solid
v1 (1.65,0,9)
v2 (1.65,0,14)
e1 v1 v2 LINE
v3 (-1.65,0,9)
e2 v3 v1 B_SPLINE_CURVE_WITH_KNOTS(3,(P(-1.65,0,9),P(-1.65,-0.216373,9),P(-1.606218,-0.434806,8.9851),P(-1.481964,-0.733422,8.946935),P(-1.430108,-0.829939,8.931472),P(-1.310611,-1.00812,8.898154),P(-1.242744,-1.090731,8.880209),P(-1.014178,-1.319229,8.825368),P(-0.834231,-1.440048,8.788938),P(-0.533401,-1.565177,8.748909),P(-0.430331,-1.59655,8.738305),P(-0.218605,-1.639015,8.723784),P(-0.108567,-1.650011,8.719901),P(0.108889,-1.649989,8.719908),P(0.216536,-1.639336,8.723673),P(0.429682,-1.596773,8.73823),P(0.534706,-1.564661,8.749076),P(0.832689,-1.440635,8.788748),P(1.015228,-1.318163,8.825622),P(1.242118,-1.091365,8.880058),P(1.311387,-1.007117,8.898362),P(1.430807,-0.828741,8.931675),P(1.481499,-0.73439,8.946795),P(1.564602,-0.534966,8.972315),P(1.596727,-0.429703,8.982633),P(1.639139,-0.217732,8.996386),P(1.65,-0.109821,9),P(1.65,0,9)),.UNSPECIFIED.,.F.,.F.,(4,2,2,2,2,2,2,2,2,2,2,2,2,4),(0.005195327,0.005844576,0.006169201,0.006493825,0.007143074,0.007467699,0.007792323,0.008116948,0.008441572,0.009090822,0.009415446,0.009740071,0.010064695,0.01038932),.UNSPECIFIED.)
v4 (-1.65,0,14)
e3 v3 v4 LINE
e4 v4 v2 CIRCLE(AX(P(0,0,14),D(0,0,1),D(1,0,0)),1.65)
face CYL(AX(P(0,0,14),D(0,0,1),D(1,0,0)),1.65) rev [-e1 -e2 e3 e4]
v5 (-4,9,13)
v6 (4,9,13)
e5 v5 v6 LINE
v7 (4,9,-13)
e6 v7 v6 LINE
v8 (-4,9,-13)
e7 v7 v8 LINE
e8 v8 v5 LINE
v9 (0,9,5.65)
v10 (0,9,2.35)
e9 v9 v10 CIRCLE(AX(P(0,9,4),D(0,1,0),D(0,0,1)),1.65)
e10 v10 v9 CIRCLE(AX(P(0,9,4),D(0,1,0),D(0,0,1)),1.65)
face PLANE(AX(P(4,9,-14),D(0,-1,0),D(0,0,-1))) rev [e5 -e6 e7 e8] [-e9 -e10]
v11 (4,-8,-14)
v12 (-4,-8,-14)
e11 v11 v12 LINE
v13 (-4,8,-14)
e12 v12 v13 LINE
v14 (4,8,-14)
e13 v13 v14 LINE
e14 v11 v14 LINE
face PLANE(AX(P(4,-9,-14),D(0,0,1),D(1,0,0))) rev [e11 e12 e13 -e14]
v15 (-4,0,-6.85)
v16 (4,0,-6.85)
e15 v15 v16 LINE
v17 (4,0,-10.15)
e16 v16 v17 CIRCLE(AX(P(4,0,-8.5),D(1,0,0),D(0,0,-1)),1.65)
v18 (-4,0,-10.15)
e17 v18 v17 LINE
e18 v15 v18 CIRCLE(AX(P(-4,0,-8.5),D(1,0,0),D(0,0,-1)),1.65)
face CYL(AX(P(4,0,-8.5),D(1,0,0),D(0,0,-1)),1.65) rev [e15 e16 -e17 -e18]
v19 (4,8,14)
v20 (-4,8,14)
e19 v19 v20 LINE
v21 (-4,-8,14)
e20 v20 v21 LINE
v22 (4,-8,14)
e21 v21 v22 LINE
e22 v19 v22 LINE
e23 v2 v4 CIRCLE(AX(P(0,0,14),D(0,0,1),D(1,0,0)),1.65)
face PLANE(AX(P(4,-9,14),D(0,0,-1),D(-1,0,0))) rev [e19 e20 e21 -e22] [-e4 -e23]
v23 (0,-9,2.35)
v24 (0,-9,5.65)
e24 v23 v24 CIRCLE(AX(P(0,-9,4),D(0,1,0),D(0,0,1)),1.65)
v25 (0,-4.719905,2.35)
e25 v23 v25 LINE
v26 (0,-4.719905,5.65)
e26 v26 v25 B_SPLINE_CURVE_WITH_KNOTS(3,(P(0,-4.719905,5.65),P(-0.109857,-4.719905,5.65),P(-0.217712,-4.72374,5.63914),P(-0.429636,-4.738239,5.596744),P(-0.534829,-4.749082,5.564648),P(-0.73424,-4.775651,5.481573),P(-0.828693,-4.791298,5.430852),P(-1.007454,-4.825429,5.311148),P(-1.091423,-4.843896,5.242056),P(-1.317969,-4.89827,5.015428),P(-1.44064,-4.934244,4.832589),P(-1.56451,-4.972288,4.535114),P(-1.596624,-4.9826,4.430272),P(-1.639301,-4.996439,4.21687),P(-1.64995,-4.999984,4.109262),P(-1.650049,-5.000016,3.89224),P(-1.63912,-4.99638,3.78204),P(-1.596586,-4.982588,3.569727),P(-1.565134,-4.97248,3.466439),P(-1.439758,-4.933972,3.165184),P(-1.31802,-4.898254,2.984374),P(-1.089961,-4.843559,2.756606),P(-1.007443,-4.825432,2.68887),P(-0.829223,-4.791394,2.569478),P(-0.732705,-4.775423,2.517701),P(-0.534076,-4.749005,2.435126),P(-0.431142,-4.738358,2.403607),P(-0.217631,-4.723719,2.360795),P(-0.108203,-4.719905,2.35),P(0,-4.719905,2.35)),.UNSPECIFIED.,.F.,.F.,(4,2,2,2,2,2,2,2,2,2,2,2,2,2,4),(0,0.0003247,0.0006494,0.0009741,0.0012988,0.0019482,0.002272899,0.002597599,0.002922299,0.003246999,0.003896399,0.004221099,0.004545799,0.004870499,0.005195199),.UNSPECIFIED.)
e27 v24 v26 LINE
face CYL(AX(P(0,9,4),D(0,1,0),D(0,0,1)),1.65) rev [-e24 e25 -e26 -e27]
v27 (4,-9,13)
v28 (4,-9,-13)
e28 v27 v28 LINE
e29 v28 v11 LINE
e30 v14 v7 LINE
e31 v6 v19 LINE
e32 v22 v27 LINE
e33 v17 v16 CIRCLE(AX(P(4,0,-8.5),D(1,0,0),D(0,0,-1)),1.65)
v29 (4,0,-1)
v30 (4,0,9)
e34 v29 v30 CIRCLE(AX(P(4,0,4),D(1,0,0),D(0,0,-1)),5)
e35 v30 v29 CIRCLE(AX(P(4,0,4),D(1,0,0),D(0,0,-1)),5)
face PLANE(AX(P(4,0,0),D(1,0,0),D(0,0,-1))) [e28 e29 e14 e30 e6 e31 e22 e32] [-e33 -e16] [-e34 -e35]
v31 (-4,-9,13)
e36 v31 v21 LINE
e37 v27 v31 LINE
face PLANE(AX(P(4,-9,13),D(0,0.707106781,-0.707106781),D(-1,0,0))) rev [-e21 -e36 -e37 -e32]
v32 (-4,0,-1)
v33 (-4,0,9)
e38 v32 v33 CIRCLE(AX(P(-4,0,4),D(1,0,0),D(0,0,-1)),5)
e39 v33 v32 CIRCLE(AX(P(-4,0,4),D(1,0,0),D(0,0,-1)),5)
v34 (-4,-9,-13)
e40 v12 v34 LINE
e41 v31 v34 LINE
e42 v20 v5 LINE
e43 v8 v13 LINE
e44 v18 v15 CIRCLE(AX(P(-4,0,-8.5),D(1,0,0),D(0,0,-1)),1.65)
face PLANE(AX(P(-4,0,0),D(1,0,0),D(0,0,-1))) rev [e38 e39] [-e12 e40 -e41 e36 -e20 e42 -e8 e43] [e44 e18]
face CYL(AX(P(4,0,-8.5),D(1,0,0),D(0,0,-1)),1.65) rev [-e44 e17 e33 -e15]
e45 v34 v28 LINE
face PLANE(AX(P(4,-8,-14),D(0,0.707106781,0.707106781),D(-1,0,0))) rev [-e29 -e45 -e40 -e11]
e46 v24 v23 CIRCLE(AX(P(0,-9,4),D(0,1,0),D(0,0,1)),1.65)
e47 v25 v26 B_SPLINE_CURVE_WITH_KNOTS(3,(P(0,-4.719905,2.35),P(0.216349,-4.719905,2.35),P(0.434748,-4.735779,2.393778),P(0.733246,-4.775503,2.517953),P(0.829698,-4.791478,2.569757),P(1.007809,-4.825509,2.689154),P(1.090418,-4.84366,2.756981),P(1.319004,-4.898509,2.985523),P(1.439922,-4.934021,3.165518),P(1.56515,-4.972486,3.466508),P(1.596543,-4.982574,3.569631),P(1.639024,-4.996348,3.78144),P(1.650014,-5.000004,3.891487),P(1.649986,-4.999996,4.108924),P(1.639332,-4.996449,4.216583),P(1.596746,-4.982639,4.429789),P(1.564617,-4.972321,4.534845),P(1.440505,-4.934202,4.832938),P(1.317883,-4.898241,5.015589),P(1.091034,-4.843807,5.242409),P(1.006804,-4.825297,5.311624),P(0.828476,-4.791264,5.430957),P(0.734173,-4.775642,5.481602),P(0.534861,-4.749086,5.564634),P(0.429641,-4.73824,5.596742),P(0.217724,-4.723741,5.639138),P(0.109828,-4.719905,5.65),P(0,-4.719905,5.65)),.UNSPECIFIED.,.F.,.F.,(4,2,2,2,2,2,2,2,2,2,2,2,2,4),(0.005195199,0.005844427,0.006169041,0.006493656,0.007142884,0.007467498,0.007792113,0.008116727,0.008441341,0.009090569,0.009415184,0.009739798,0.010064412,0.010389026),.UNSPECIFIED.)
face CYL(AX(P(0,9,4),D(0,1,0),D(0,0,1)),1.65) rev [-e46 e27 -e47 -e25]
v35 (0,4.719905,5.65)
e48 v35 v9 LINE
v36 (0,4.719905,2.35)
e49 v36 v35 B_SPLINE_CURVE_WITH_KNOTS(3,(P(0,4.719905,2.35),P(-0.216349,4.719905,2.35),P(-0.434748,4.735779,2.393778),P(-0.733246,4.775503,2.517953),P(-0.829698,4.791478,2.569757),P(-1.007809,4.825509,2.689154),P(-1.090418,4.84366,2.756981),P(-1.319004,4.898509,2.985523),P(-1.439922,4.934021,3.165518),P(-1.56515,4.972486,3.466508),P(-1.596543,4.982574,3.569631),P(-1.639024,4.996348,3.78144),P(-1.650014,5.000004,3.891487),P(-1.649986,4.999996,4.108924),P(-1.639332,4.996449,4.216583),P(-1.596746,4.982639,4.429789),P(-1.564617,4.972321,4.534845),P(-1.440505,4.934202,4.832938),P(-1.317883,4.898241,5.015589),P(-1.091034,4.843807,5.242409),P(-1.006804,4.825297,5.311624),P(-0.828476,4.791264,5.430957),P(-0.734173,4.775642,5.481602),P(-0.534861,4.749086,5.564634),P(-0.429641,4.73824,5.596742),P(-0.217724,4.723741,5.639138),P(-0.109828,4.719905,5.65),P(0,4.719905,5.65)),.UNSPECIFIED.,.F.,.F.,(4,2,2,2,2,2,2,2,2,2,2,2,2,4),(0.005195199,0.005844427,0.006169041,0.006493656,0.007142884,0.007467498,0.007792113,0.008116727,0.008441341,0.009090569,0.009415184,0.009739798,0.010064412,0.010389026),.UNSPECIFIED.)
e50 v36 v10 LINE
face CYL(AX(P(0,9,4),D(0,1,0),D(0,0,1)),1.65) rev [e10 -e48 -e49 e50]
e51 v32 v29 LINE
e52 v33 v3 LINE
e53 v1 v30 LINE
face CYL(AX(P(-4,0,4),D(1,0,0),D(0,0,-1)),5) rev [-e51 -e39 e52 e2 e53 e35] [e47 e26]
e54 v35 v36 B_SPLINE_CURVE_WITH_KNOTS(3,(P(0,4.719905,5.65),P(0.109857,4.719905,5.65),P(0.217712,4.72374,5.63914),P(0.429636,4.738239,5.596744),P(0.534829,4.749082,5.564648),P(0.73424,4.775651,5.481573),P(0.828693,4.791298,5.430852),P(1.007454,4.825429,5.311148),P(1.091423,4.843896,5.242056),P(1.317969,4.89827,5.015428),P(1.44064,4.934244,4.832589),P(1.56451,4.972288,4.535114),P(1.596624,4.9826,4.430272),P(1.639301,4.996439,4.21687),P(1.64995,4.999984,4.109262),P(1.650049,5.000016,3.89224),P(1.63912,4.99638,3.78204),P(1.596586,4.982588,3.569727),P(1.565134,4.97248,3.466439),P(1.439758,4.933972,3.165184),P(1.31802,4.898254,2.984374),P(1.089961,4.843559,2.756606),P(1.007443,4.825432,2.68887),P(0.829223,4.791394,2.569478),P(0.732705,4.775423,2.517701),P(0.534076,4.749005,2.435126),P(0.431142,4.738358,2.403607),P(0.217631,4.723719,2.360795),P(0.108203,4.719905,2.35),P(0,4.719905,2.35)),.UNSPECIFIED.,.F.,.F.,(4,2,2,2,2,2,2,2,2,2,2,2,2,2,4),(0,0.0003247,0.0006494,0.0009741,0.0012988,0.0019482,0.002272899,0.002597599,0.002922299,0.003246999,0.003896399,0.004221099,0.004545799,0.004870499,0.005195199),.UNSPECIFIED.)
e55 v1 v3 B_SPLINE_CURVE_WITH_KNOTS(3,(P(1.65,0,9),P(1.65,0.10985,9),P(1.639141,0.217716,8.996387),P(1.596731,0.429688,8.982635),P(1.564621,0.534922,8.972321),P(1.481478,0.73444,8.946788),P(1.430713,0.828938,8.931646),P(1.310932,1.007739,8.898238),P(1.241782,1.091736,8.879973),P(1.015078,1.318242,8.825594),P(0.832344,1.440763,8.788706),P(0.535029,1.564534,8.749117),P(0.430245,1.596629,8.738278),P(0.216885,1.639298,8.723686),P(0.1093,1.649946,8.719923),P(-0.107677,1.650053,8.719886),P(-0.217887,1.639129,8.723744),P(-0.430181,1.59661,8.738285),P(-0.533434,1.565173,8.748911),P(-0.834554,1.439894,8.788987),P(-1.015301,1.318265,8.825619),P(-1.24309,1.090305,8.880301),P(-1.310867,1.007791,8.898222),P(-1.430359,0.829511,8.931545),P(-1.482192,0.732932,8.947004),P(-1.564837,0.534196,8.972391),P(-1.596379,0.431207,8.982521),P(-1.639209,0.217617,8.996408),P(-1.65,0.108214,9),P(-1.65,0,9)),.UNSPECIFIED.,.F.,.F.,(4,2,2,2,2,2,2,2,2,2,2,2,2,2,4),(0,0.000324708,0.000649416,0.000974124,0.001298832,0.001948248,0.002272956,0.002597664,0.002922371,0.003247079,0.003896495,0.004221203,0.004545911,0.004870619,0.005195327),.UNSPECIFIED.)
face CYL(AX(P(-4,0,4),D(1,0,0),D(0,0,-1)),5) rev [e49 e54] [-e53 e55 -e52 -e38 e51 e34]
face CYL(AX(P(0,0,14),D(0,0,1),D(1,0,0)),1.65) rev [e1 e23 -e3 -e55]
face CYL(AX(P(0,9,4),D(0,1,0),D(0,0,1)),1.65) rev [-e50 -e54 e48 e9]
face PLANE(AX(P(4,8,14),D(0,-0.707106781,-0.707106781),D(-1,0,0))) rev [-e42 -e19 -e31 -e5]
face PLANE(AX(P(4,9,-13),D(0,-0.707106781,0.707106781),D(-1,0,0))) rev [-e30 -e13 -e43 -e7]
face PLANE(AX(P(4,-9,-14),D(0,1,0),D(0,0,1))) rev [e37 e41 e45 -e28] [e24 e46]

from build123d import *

# Parameters (mm, degrees)
SKETCH_1_W              = 28
SKETCH_1_H              = 18
EXTRUDE_1_DEPTH         = 4
SKETCH_2_R              = 5
CUT_EXTRUDE_1_DEPTH     = 19.466185313
HOLE_WIZARD_M4_1_REACH  = 31.682
HOLE_WIZARD_M4_1_BORE_R = 1.65
HOLE_WIZARD_M4_2_D      = 3.3
HOLE_WIZARD_M4_3_D      = 3.3
CHAMFER_1_SIZE          = 1


with BuildPart() as part:
    # 草图1 → 凸台-拉伸1 (new, symmetric)
    with BuildSketch(Plane(origin=(0, 0, 0), x_dir=(0, 0, -1), z_dir=(1, 0, 0))):
        Rectangle(SKETCH_1_W, SKETCH_1_H)
    extrude(amount=EXTRUDE_1_DEPTH, both=True)

    # 草图2 → 切除-拉伸1 (cut, through all)
    with BuildSketch(Plane(origin=(4, 0, 0), x_dir=(0, 0, -1), z_dir=(1, 0, 0))):
        with Locations((-4, 0)):
            Circle(SKETCH_2_R)
    extrude(amount=-CUT_EXTRUDE_1_DEPTH, mode=Mode.SUBTRACT)

    # M4 螺纹孔1 bore → M4 螺纹孔1 (cut, up to next)
    with BuildSketch(Plane.XY.offset(14), mode=Mode.PRIVATE) as hole_wizard_m4_1_sk1:
        Circle(HOLE_WIZARD_M4_1_BORE_R)
    hole_wizard_m4_1_tool1 = extrude(hole_wizard_m4_1_sk1.sketch, amount=-HOLE_WIZARD_M4_1_REACH, mode=Mode.PRIVATE) & part.part
    add(hole_wizard_m4_1_tool1.solids().sort_by_distance((0, 0, 14))[0], mode=Mode.SUBTRACT)

    # M4 螺纹孔2 (through all)
    with Locations(Plane(origin=(4, 0, 0), x_dir=(0, 0, -1), z_dir=(1, 0, 0))):
        with Locations((8.5, 0)):
            Hole(HOLE_WIZARD_M4_2_D / 2)

    # M4 螺纹孔3 (through all)
    with Locations(Plane(origin=(0, 9, 0), x_dir=(1, 0, 0), z_dir=(0, 1, 0))):
        with Locations((0, -4)):
            Hole(HOLE_WIZARD_M4_3_D / 2)

    # 倒角1
    chamfer_1_edges = [part.edges().sort_by_distance(p)[0] for p in [
        (0, 9, 14),
        (0, 9, -14),
        (0, -9, -14),
        (0, -9, 14),
    ]]
    chamfer(chamfer_1_edges, length=CHAMFER_1_SIZE)


solid = part.part
